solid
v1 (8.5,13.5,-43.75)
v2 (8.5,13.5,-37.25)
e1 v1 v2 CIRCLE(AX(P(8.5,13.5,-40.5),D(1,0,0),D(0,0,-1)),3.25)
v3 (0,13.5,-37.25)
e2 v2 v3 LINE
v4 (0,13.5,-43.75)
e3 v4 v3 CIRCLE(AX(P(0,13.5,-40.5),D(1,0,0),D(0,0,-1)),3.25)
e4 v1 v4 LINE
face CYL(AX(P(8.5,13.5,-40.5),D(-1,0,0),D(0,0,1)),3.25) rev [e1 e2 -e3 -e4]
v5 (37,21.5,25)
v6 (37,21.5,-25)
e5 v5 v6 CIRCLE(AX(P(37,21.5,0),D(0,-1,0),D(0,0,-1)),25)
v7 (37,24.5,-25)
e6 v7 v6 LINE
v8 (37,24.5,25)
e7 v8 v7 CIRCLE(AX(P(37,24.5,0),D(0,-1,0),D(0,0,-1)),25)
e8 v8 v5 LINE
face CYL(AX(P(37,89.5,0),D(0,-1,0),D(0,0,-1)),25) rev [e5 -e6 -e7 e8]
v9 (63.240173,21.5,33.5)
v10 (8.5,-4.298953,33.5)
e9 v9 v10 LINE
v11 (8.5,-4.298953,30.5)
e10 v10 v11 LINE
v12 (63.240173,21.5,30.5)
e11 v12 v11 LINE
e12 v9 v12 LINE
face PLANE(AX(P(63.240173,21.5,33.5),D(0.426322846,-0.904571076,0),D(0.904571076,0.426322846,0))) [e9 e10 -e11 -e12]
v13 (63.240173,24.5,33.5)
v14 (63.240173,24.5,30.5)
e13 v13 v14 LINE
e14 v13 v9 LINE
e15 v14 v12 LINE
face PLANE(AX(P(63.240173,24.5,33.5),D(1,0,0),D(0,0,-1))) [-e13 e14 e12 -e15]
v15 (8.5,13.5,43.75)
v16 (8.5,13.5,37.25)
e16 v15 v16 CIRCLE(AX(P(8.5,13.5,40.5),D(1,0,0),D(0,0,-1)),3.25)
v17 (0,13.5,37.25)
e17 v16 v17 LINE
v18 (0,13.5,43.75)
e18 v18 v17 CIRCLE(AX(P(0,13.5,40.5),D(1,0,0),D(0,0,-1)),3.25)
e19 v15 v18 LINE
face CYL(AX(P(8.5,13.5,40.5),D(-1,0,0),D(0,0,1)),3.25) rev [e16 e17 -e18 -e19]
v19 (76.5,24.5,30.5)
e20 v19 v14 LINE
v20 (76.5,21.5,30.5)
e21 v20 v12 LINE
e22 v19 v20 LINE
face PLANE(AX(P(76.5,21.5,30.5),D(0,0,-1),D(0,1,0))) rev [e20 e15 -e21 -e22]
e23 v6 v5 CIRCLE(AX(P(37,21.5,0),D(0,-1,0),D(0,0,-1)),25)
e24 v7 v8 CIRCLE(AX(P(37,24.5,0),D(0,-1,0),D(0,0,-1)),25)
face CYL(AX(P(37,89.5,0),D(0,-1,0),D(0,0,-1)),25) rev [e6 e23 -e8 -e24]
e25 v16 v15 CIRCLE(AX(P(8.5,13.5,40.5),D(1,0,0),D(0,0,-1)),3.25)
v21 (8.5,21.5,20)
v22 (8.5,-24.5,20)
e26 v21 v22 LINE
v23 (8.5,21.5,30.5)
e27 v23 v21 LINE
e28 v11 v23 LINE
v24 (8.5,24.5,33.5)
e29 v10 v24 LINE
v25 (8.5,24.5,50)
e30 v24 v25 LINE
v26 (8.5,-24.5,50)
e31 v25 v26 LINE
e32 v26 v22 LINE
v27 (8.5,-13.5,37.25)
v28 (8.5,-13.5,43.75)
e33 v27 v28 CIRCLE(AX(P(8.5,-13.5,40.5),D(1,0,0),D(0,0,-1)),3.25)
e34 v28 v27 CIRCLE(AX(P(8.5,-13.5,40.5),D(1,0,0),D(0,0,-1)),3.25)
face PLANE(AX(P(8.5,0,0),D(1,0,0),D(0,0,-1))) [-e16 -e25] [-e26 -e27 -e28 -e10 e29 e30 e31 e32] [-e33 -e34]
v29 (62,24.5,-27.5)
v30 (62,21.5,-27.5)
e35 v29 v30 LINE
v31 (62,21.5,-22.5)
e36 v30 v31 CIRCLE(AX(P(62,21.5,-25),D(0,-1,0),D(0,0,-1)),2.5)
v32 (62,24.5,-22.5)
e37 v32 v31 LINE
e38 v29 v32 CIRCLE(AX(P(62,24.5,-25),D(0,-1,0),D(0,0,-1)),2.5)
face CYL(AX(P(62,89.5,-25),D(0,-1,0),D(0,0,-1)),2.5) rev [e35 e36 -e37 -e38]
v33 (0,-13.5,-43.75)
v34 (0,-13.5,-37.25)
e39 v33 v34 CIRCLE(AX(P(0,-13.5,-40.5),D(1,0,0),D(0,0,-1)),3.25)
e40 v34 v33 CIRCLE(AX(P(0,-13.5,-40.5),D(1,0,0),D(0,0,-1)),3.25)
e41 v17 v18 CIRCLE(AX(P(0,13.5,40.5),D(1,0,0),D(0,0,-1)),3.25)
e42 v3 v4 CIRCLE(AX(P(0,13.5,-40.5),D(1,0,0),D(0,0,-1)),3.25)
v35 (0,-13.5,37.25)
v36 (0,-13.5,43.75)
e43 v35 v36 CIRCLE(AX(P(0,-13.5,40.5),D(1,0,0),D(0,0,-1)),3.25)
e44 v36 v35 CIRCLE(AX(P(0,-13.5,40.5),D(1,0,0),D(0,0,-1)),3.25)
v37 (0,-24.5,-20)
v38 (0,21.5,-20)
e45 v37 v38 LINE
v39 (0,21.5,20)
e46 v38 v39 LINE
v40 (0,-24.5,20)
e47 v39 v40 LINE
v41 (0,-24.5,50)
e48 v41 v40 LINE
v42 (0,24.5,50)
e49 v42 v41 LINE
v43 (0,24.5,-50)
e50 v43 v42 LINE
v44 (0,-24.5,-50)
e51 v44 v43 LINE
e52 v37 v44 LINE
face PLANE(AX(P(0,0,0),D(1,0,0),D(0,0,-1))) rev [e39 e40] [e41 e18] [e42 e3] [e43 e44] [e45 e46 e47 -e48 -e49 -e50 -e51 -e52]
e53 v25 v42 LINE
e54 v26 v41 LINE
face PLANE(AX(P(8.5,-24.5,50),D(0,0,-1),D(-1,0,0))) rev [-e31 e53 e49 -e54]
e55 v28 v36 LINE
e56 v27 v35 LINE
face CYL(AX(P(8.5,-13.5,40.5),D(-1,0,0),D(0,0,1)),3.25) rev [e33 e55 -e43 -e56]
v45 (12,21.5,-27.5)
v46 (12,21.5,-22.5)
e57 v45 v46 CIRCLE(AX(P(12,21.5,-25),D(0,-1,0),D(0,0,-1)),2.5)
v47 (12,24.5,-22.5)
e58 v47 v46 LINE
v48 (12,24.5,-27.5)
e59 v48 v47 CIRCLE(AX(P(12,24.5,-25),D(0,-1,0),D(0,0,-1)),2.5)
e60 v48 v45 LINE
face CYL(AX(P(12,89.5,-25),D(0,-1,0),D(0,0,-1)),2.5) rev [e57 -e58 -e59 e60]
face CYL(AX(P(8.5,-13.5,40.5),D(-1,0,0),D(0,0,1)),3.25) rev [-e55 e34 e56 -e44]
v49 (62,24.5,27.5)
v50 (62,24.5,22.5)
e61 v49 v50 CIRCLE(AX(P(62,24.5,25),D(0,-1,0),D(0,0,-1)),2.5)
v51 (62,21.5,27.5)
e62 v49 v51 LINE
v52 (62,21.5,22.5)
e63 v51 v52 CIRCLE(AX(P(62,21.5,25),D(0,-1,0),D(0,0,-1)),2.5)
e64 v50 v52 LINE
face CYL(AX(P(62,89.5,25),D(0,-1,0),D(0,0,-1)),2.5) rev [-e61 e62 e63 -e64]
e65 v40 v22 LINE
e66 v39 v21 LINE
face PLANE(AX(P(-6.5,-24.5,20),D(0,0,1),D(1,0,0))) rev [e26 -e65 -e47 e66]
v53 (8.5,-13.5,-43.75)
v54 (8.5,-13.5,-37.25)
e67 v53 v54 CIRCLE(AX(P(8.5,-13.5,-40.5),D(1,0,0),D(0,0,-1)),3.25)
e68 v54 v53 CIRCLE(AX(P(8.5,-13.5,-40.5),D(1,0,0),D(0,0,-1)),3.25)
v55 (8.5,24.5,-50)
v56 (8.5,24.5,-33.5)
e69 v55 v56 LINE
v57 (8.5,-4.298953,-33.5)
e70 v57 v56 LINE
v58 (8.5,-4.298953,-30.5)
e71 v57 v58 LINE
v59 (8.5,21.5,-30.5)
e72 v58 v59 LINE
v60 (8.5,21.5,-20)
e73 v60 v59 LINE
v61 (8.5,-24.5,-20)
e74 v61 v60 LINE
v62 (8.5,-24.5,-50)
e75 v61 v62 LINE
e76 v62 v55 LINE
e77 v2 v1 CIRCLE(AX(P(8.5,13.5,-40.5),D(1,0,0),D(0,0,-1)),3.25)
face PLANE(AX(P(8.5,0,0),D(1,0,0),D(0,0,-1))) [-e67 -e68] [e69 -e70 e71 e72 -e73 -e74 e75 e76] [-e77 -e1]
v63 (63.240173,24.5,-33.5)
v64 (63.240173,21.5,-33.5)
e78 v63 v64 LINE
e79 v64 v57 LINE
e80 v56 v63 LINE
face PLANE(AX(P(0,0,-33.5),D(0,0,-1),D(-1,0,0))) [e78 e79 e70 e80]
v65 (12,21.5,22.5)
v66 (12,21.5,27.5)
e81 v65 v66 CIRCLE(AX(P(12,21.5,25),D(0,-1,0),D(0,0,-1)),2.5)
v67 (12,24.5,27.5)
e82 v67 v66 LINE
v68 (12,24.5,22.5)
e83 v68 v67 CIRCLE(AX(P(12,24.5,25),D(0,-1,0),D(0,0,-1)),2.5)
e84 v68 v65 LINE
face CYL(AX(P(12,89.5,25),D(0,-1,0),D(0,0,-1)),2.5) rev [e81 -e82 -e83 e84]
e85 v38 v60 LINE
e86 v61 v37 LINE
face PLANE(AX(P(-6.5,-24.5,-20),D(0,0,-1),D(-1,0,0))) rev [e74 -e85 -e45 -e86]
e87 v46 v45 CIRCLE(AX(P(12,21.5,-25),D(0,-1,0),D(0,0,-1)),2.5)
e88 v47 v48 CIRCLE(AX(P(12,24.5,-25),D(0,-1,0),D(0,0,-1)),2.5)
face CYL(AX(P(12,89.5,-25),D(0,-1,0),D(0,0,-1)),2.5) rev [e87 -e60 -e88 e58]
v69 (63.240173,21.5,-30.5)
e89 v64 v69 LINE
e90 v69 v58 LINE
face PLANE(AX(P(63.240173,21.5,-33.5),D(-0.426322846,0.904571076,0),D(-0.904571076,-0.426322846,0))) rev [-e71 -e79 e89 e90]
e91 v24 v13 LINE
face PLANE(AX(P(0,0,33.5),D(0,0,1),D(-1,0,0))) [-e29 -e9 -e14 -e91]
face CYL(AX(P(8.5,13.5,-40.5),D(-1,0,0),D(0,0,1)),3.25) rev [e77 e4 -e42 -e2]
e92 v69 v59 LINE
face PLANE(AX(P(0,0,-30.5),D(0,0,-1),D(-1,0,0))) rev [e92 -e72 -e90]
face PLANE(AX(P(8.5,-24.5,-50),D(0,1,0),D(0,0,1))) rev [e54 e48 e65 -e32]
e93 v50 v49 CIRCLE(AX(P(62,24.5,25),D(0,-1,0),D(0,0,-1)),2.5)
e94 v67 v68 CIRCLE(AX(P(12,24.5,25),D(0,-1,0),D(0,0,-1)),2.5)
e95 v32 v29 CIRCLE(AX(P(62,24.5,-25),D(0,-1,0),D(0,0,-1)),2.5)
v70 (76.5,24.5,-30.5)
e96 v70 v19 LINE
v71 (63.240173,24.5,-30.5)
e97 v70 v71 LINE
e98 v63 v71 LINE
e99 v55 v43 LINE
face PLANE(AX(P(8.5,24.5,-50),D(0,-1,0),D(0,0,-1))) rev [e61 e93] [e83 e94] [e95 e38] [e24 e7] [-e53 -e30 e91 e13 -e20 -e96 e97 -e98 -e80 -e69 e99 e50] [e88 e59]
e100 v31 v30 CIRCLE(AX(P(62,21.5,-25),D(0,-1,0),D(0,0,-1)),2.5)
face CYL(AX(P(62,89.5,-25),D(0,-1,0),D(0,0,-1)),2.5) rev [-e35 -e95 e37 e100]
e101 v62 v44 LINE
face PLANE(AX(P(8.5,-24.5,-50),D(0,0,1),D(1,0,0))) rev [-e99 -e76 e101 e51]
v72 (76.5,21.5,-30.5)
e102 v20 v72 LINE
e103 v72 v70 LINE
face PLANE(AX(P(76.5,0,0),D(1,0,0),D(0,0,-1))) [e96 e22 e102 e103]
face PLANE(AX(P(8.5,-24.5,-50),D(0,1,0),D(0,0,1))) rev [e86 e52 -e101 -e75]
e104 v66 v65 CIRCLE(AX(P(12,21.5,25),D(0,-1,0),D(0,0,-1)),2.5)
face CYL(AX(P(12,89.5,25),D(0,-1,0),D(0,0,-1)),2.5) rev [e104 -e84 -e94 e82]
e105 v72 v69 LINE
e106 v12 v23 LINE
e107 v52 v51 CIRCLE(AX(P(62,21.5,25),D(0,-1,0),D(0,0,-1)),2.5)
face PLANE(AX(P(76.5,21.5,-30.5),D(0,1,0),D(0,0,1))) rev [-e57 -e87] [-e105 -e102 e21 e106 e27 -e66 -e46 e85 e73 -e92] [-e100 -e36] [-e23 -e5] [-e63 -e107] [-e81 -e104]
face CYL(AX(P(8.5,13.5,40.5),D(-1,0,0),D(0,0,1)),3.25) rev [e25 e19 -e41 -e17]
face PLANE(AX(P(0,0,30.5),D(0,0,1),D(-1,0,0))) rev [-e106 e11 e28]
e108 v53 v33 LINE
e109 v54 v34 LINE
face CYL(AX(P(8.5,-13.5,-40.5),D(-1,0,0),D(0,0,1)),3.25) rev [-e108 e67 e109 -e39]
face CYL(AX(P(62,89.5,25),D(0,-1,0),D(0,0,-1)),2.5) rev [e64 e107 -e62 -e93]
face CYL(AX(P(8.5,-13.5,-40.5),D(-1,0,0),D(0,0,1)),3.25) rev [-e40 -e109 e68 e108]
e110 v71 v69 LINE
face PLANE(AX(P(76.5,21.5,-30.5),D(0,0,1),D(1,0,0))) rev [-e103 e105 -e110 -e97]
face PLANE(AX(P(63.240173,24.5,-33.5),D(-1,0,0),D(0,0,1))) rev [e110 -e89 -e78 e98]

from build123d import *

# Parameters (mm, degrees)
SKETCH_1_W          = 100
SKETCH_1_H          = 49
SKETCH_1_R          = 3.25
EXTRUDE_1_DEPTH     = 8.5
SKETCH_2_W          = 61
SKETCH_2_H          = 3
EXTRUDE_2_DEPTH     = 68
SKETCH_3_R          = 25
CUT_EXTRUDE_1_DEPTH = 68
SKETCH_4_R          = 2.5
CUT_EXTRUDE_2_DEPTH = 68
SKETCH_5_W          = 40
SKETCH_5_H          = 46
CUT_EXTRUDE_3_DEPTH = 15
EXTRUDE_3_DEPTH     = 3


with BuildPart() as part:
    # 草图1 → 凸台-拉伸1 (new body)
    with BuildSketch(Plane(origin=(0, 0, 0), x_dir=(0, 0, -1), z_dir=(1, 0, 0))):
        Rectangle(SKETCH_1_W, SKETCH_1_H)
        with Locations((-40.5, 13.5)):
            Circle(SKETCH_1_R, mode=Mode.SUBTRACT)
        with Locations((40.5, 13.5)):
            Circle(SKETCH_1_R, mode=Mode.SUBTRACT)
        with Locations((40.5, -13.5)):
            Circle(SKETCH_1_R, mode=Mode.SUBTRACT)
        with Locations((-40.5, -13.5)):
            Circle(SKETCH_1_R, mode=Mode.SUBTRACT)
    extrude(amount=EXTRUDE_1_DEPTH)

    # 草图2 → 凸台-拉伸2 (add)
    with BuildSketch(Plane(origin=(8.5, 0, 0), x_dir=(0, 0, -1), z_dir=(1, 0, 0))):
        with Locations((0, 23)):
            Rectangle(SKETCH_2_W, SKETCH_2_H)
    extrude(amount=EXTRUDE_2_DEPTH)

    # 草图3 → 切除-拉伸1 (cut)
    with BuildSketch(Plane.XZ.offset(-21.5)):
        with Locations(Location((37, 0, 0), (0, 0, 270))):
            Circle(SKETCH_3_R)
    extrude(amount=-CUT_EXTRUDE_1_DEPTH, mode=Mode.SUBTRACT)

    # 草图4 → 切除-拉伸2 (cut)
    with BuildSketch(Plane.XZ.offset(-21.5)):
        with Locations(Location((12, 25, 0), (0, 0, 270))):
            Circle(SKETCH_4_R)
        with Locations(Location((62, 25, 0), (0, 0, 270))):
            Circle(SKETCH_4_R)
        with Locations(Location((62, -25, 0), (0, 0, 270))):
            Circle(SKETCH_4_R)
        with Locations(Location((12, -25, 0), (0, 0, 270))):
            Circle(SKETCH_4_R)
    extrude(amount=-CUT_EXTRUDE_2_DEPTH, mode=Mode.SUBTRACT)

    # 草图5 → 切除-拉伸3 (cut)
    with BuildSketch(Plane(origin=(8.5, 0, 0), x_dir=(0, 0, -1), z_dir=(1, 0, 0))):
        with Locations((0, -1.5)):
            Rectangle(SKETCH_5_W, SKETCH_5_H)
    extrude(amount=-CUT_EXTRUDE_3_DEPTH, mode=Mode.SUBTRACT)

    # 草图6 → 凸台-拉伸3 (add)
    with BuildSketch(Plane(origin=(0, 0, -30.5), x_dir=(-1, 0, 0), z_dir=(0, 0, -1))):
        Polygon((-63.240172939, 24.5), (-63.240172939, 21.5), (-8.5, -4.29895258), (-8.5, 24.5), align=None)
    extrude_3 = extrude(amount=EXTRUDE_3_DEPTH)

    # 镜向1: 凸台-拉伸3 across plane
    add(extrude_3.mirror(Plane.XY))


solid = part.part
